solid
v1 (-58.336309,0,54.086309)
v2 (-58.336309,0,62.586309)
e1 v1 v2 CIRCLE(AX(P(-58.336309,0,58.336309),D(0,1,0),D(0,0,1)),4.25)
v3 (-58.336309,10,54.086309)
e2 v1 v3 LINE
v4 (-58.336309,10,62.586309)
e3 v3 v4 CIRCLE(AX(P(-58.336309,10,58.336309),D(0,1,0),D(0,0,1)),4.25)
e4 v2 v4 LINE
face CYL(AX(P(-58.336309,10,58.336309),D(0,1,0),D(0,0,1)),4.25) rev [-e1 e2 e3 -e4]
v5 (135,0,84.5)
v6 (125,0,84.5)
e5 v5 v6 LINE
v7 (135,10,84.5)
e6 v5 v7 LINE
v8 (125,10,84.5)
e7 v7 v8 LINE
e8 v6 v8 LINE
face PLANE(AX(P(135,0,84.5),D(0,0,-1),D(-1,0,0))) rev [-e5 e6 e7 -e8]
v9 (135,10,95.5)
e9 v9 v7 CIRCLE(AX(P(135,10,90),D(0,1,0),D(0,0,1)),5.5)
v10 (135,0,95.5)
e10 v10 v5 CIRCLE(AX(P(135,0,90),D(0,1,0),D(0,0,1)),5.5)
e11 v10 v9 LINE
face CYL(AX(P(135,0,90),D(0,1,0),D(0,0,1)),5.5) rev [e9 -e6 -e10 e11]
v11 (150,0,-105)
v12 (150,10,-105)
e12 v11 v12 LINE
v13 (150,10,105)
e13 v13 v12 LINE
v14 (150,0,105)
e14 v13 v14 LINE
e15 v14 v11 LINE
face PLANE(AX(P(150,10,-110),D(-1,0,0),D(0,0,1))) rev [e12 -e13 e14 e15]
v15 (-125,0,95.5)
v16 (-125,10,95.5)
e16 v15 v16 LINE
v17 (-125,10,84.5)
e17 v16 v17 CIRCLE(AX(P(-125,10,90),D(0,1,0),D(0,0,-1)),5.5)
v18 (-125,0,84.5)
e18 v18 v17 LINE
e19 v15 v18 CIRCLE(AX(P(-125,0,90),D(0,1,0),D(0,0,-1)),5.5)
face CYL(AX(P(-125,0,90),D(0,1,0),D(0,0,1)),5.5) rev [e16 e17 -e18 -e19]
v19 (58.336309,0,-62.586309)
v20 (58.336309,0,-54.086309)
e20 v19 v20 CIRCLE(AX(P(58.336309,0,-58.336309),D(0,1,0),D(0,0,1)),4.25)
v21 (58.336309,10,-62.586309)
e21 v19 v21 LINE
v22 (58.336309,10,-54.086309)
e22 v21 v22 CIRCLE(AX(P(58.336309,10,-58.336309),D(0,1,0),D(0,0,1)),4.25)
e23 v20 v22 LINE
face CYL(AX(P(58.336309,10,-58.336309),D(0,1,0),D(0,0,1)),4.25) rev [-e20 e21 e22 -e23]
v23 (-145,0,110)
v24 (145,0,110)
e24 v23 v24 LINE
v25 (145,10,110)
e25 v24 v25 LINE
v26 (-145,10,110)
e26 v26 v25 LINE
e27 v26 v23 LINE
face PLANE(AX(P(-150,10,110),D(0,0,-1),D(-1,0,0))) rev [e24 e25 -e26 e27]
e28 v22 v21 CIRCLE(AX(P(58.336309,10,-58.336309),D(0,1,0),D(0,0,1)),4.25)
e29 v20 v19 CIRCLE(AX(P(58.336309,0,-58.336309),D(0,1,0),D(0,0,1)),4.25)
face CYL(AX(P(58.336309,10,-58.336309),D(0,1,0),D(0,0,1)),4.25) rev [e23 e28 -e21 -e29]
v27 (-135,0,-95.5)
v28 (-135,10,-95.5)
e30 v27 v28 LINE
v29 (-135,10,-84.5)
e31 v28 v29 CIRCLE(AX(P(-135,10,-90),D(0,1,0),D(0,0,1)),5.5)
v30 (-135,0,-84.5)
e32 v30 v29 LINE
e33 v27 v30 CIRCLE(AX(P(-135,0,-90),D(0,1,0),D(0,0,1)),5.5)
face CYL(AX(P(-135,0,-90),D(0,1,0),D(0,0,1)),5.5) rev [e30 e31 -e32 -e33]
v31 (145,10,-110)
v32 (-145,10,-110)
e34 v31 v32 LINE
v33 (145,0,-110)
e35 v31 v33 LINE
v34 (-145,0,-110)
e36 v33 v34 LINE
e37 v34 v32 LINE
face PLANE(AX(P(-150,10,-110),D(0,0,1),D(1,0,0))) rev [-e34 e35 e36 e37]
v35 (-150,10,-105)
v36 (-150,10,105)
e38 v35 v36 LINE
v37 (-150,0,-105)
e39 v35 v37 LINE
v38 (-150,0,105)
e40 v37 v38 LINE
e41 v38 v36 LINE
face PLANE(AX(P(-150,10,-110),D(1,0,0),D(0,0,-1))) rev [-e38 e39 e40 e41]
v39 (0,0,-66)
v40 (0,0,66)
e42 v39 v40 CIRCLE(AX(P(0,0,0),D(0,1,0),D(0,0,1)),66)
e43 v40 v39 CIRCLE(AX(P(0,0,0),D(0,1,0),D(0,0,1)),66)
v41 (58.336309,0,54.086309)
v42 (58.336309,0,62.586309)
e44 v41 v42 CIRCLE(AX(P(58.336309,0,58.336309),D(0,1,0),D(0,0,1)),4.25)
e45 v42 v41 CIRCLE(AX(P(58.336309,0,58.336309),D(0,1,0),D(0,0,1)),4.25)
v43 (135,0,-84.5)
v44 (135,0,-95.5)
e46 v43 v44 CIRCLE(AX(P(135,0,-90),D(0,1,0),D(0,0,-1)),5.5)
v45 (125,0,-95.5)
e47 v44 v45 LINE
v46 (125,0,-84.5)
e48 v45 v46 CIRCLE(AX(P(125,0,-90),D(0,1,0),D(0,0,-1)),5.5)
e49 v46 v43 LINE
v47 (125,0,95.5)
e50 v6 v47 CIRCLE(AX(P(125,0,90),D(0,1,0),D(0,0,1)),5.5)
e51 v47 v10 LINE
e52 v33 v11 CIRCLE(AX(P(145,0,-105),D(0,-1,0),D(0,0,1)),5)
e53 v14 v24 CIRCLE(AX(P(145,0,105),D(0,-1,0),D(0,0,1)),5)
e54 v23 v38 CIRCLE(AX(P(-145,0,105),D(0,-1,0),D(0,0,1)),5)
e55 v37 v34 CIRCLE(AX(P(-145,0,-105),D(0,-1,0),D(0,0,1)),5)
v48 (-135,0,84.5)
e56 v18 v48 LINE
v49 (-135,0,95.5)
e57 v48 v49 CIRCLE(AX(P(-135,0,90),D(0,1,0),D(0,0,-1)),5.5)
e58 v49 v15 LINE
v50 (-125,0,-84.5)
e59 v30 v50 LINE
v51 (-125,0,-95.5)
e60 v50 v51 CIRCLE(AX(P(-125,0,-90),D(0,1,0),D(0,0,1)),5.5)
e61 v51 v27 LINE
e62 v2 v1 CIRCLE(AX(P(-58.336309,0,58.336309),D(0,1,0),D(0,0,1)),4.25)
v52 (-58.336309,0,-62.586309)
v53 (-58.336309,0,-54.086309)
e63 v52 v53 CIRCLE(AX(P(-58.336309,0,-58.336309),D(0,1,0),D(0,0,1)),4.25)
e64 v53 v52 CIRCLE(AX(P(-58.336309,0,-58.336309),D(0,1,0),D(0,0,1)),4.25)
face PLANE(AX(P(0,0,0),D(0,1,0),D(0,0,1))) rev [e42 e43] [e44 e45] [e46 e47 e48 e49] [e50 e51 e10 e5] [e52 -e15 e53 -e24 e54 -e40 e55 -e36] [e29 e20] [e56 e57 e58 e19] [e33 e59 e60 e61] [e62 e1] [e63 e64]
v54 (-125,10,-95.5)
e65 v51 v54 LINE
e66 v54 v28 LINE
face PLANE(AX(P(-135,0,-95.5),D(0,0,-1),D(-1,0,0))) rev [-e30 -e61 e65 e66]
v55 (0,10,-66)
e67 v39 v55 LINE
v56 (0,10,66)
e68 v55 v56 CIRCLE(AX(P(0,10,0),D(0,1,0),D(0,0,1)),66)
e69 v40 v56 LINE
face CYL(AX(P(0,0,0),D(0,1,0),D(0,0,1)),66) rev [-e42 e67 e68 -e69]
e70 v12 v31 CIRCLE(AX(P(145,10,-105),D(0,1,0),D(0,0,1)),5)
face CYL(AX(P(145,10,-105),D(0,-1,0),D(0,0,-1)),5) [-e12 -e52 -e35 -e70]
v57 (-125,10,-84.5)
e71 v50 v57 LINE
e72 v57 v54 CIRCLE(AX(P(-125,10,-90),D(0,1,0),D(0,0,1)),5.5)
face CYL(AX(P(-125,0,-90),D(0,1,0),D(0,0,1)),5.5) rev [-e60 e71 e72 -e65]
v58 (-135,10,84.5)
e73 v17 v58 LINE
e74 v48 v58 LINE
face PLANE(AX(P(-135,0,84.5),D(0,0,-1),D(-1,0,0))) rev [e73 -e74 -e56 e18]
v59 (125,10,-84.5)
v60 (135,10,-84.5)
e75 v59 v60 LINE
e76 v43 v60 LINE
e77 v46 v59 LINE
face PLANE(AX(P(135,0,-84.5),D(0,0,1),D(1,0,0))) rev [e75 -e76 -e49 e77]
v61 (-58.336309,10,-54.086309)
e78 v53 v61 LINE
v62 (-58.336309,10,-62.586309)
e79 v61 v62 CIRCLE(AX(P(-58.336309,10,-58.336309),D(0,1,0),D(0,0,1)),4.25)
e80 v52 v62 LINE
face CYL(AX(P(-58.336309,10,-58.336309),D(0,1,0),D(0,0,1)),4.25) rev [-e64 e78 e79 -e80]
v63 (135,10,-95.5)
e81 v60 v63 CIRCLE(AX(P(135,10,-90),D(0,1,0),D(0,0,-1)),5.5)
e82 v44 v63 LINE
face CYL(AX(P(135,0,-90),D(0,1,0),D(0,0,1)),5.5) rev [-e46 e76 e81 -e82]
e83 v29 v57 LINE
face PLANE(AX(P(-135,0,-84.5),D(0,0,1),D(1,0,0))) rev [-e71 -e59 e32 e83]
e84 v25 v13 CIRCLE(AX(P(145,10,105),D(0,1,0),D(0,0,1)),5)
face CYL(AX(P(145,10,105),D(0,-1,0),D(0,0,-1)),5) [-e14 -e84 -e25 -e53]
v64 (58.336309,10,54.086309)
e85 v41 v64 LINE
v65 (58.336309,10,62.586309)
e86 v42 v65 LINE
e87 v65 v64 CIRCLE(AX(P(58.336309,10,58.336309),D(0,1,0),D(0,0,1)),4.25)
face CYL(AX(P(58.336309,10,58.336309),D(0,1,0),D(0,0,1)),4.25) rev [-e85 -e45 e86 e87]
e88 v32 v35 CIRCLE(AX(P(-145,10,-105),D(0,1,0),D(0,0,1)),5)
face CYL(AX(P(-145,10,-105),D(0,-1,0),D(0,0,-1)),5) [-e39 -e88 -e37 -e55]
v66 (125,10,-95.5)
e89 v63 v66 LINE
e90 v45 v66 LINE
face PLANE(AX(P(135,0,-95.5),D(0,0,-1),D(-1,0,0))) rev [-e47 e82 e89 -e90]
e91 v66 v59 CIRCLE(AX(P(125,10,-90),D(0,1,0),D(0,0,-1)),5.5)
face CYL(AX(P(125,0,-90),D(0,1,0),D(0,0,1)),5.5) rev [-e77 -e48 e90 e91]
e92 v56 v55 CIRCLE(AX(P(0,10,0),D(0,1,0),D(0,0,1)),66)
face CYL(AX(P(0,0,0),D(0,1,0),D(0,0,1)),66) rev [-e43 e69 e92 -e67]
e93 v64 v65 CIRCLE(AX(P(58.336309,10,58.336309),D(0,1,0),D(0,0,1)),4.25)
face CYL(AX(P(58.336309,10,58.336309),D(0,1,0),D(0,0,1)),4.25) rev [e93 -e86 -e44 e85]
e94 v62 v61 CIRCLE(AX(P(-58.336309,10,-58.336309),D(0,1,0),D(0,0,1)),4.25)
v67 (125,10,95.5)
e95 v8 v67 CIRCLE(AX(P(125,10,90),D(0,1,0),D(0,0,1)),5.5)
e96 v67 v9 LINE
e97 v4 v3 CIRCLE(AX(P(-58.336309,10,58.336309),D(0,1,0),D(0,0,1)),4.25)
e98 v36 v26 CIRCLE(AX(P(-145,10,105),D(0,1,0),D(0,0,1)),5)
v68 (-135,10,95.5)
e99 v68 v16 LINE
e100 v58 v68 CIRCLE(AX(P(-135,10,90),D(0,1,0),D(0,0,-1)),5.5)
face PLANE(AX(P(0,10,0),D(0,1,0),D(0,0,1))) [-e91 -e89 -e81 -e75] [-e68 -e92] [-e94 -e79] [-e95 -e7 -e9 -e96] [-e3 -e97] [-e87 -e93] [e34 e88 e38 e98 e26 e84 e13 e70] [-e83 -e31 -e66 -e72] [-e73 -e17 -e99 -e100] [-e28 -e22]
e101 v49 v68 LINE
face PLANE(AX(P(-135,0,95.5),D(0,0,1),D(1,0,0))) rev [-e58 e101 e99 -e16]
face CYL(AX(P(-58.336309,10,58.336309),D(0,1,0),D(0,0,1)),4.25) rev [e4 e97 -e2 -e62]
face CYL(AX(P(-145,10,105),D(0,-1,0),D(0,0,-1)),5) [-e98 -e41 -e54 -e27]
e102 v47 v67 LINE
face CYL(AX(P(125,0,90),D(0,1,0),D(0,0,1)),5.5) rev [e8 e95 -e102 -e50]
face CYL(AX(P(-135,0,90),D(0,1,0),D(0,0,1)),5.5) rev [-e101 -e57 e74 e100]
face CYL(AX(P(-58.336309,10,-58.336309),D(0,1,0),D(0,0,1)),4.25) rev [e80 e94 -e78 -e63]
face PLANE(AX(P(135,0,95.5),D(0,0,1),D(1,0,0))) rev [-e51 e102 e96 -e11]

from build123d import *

# Parameters (mm, degrees)
SKETCH1_W              = 300
SKETCH1_H              = 220
BOSS_EXTRUDE1_DEPTH    = 10
SKETCH3_R              = 66
CUT_EXTRUDE1_DEPTH     = 187.279360102
M10_TAPPED_HOLE1_D     = 8.5
M10_TAPPED_HOLE1_DEPTH = 24.5
M10_TAPPED_HOLE1_TIP   = 2.553657631
CUT_EXTRUDE2_DEPTH     = 187.279360102
FILLET1_R              = 5


with BuildPart() as part:
    # Sketch1 → Boss-Extrude1 (new body)
    with BuildSketch(Plane(origin=(0, 0, 0), x_dir=(1, 0, 0), z_dir=(0, 1, 0))):
        Rectangle(SKETCH1_W, SKETCH1_H)
    extrude(amount=BOSS_EXTRUDE1_DEPTH)

    # Sketch3 → Cut-Extrude1 (cut, through all)
    with BuildSketch(Plane(origin=(0, 10, 0), x_dir=(1, 0, 0), z_dir=(0, 1, 0))):
        with Locations(Location((0, 0, 0), (0, 0, 270))):
            Circle(SKETCH3_R)
    extrude(amount=-CUT_EXTRUDE1_DEPTH, mode=Mode.SUBTRACT)

    # M10 Tapped Hole1
    with Locations(Plane(origin=(0, 10, 0), x_dir=(1, 0, 0), z_dir=(0, 1, 0))):
        with Locations((-58.336309448, -58.336309448), (-58.336309448, 58.336309448), (58.336309448, 58.336309448), (58.336309448, -58.336309448)):
            Hole(M10_TAPPED_HOLE1_D / 2, depth=M10_TAPPED_HOLE1_DEPTH)
            with Locations((0, 0, -(M10_TAPPED_HOLE1_DEPTH + M10_TAPPED_HOLE1_TIP / 2))):  # 118° drill point
                Cone(0, M10_TAPPED_HOLE1_D / 2, M10_TAPPED_HOLE1_TIP, mode=Mode.SUBTRACT)

    # Sketch6 → Cut-Extrude2 (cut, through all)
    with BuildSketch(Plane(origin=(0, 10, 0), x_dir=(1, 0, 0), z_dir=(0, 1, 0))):
        with BuildLine():
            Line((-135, 95.5), (-125, 95.5))
            ThreePointArc((-125, 95.5), (-119.5, 90), (-125, 84.5))
            Line((-125, 84.5), (-135, 84.5))
            ThreePointArc((-135, 84.5), (-140.5, 90), (-135, 95.5))
        make_face()
        with BuildLine():
            Line((135, 95.5), (125, 95.5))
            ThreePointArc((125, 95.5), (119.5, 90), (125, 84.5))
            Line((125, 84.5), (135, 84.5))
            ThreePointArc((135, 84.5), (140.5, 90), (135, 95.5))
        make_face()
        with BuildLine():
            Line((135, -95.5), (125, -95.5))
            ThreePointArc((125, -95.5), (119.5, -90), (125, -84.5))
            Line((125, -84.5), (135, -84.5))
            ThreePointArc((135, -84.5), (140.5, -90), (135, -95.5))
        make_face()
        with BuildLine():
            Line((-135, -95.5), (-125, -95.5))
            ThreePointArc((-125, -95.5), (-119.5, -90), (-125, -84.5))
            Line((-125, -84.5), (-135, -84.5))
            ThreePointArc((-135, -84.5), (-140.5, -90), (-135, -95.5))
        make_face()
    extrude(amount=-CUT_EXTRUDE2_DEPTH, mode=Mode.SUBTRACT)

    # Fillet1
    fillet1_edges = [part.edges().sort_by_distance(p)[0] for p in [
        (150, 5, 110),
        (-150, 5, 110),
        (-150, 5, -110),
        (150, 5, -110),
    ]]
    fillet(fillet1_edges, radius=FILLET1_R)


solid = part.part
